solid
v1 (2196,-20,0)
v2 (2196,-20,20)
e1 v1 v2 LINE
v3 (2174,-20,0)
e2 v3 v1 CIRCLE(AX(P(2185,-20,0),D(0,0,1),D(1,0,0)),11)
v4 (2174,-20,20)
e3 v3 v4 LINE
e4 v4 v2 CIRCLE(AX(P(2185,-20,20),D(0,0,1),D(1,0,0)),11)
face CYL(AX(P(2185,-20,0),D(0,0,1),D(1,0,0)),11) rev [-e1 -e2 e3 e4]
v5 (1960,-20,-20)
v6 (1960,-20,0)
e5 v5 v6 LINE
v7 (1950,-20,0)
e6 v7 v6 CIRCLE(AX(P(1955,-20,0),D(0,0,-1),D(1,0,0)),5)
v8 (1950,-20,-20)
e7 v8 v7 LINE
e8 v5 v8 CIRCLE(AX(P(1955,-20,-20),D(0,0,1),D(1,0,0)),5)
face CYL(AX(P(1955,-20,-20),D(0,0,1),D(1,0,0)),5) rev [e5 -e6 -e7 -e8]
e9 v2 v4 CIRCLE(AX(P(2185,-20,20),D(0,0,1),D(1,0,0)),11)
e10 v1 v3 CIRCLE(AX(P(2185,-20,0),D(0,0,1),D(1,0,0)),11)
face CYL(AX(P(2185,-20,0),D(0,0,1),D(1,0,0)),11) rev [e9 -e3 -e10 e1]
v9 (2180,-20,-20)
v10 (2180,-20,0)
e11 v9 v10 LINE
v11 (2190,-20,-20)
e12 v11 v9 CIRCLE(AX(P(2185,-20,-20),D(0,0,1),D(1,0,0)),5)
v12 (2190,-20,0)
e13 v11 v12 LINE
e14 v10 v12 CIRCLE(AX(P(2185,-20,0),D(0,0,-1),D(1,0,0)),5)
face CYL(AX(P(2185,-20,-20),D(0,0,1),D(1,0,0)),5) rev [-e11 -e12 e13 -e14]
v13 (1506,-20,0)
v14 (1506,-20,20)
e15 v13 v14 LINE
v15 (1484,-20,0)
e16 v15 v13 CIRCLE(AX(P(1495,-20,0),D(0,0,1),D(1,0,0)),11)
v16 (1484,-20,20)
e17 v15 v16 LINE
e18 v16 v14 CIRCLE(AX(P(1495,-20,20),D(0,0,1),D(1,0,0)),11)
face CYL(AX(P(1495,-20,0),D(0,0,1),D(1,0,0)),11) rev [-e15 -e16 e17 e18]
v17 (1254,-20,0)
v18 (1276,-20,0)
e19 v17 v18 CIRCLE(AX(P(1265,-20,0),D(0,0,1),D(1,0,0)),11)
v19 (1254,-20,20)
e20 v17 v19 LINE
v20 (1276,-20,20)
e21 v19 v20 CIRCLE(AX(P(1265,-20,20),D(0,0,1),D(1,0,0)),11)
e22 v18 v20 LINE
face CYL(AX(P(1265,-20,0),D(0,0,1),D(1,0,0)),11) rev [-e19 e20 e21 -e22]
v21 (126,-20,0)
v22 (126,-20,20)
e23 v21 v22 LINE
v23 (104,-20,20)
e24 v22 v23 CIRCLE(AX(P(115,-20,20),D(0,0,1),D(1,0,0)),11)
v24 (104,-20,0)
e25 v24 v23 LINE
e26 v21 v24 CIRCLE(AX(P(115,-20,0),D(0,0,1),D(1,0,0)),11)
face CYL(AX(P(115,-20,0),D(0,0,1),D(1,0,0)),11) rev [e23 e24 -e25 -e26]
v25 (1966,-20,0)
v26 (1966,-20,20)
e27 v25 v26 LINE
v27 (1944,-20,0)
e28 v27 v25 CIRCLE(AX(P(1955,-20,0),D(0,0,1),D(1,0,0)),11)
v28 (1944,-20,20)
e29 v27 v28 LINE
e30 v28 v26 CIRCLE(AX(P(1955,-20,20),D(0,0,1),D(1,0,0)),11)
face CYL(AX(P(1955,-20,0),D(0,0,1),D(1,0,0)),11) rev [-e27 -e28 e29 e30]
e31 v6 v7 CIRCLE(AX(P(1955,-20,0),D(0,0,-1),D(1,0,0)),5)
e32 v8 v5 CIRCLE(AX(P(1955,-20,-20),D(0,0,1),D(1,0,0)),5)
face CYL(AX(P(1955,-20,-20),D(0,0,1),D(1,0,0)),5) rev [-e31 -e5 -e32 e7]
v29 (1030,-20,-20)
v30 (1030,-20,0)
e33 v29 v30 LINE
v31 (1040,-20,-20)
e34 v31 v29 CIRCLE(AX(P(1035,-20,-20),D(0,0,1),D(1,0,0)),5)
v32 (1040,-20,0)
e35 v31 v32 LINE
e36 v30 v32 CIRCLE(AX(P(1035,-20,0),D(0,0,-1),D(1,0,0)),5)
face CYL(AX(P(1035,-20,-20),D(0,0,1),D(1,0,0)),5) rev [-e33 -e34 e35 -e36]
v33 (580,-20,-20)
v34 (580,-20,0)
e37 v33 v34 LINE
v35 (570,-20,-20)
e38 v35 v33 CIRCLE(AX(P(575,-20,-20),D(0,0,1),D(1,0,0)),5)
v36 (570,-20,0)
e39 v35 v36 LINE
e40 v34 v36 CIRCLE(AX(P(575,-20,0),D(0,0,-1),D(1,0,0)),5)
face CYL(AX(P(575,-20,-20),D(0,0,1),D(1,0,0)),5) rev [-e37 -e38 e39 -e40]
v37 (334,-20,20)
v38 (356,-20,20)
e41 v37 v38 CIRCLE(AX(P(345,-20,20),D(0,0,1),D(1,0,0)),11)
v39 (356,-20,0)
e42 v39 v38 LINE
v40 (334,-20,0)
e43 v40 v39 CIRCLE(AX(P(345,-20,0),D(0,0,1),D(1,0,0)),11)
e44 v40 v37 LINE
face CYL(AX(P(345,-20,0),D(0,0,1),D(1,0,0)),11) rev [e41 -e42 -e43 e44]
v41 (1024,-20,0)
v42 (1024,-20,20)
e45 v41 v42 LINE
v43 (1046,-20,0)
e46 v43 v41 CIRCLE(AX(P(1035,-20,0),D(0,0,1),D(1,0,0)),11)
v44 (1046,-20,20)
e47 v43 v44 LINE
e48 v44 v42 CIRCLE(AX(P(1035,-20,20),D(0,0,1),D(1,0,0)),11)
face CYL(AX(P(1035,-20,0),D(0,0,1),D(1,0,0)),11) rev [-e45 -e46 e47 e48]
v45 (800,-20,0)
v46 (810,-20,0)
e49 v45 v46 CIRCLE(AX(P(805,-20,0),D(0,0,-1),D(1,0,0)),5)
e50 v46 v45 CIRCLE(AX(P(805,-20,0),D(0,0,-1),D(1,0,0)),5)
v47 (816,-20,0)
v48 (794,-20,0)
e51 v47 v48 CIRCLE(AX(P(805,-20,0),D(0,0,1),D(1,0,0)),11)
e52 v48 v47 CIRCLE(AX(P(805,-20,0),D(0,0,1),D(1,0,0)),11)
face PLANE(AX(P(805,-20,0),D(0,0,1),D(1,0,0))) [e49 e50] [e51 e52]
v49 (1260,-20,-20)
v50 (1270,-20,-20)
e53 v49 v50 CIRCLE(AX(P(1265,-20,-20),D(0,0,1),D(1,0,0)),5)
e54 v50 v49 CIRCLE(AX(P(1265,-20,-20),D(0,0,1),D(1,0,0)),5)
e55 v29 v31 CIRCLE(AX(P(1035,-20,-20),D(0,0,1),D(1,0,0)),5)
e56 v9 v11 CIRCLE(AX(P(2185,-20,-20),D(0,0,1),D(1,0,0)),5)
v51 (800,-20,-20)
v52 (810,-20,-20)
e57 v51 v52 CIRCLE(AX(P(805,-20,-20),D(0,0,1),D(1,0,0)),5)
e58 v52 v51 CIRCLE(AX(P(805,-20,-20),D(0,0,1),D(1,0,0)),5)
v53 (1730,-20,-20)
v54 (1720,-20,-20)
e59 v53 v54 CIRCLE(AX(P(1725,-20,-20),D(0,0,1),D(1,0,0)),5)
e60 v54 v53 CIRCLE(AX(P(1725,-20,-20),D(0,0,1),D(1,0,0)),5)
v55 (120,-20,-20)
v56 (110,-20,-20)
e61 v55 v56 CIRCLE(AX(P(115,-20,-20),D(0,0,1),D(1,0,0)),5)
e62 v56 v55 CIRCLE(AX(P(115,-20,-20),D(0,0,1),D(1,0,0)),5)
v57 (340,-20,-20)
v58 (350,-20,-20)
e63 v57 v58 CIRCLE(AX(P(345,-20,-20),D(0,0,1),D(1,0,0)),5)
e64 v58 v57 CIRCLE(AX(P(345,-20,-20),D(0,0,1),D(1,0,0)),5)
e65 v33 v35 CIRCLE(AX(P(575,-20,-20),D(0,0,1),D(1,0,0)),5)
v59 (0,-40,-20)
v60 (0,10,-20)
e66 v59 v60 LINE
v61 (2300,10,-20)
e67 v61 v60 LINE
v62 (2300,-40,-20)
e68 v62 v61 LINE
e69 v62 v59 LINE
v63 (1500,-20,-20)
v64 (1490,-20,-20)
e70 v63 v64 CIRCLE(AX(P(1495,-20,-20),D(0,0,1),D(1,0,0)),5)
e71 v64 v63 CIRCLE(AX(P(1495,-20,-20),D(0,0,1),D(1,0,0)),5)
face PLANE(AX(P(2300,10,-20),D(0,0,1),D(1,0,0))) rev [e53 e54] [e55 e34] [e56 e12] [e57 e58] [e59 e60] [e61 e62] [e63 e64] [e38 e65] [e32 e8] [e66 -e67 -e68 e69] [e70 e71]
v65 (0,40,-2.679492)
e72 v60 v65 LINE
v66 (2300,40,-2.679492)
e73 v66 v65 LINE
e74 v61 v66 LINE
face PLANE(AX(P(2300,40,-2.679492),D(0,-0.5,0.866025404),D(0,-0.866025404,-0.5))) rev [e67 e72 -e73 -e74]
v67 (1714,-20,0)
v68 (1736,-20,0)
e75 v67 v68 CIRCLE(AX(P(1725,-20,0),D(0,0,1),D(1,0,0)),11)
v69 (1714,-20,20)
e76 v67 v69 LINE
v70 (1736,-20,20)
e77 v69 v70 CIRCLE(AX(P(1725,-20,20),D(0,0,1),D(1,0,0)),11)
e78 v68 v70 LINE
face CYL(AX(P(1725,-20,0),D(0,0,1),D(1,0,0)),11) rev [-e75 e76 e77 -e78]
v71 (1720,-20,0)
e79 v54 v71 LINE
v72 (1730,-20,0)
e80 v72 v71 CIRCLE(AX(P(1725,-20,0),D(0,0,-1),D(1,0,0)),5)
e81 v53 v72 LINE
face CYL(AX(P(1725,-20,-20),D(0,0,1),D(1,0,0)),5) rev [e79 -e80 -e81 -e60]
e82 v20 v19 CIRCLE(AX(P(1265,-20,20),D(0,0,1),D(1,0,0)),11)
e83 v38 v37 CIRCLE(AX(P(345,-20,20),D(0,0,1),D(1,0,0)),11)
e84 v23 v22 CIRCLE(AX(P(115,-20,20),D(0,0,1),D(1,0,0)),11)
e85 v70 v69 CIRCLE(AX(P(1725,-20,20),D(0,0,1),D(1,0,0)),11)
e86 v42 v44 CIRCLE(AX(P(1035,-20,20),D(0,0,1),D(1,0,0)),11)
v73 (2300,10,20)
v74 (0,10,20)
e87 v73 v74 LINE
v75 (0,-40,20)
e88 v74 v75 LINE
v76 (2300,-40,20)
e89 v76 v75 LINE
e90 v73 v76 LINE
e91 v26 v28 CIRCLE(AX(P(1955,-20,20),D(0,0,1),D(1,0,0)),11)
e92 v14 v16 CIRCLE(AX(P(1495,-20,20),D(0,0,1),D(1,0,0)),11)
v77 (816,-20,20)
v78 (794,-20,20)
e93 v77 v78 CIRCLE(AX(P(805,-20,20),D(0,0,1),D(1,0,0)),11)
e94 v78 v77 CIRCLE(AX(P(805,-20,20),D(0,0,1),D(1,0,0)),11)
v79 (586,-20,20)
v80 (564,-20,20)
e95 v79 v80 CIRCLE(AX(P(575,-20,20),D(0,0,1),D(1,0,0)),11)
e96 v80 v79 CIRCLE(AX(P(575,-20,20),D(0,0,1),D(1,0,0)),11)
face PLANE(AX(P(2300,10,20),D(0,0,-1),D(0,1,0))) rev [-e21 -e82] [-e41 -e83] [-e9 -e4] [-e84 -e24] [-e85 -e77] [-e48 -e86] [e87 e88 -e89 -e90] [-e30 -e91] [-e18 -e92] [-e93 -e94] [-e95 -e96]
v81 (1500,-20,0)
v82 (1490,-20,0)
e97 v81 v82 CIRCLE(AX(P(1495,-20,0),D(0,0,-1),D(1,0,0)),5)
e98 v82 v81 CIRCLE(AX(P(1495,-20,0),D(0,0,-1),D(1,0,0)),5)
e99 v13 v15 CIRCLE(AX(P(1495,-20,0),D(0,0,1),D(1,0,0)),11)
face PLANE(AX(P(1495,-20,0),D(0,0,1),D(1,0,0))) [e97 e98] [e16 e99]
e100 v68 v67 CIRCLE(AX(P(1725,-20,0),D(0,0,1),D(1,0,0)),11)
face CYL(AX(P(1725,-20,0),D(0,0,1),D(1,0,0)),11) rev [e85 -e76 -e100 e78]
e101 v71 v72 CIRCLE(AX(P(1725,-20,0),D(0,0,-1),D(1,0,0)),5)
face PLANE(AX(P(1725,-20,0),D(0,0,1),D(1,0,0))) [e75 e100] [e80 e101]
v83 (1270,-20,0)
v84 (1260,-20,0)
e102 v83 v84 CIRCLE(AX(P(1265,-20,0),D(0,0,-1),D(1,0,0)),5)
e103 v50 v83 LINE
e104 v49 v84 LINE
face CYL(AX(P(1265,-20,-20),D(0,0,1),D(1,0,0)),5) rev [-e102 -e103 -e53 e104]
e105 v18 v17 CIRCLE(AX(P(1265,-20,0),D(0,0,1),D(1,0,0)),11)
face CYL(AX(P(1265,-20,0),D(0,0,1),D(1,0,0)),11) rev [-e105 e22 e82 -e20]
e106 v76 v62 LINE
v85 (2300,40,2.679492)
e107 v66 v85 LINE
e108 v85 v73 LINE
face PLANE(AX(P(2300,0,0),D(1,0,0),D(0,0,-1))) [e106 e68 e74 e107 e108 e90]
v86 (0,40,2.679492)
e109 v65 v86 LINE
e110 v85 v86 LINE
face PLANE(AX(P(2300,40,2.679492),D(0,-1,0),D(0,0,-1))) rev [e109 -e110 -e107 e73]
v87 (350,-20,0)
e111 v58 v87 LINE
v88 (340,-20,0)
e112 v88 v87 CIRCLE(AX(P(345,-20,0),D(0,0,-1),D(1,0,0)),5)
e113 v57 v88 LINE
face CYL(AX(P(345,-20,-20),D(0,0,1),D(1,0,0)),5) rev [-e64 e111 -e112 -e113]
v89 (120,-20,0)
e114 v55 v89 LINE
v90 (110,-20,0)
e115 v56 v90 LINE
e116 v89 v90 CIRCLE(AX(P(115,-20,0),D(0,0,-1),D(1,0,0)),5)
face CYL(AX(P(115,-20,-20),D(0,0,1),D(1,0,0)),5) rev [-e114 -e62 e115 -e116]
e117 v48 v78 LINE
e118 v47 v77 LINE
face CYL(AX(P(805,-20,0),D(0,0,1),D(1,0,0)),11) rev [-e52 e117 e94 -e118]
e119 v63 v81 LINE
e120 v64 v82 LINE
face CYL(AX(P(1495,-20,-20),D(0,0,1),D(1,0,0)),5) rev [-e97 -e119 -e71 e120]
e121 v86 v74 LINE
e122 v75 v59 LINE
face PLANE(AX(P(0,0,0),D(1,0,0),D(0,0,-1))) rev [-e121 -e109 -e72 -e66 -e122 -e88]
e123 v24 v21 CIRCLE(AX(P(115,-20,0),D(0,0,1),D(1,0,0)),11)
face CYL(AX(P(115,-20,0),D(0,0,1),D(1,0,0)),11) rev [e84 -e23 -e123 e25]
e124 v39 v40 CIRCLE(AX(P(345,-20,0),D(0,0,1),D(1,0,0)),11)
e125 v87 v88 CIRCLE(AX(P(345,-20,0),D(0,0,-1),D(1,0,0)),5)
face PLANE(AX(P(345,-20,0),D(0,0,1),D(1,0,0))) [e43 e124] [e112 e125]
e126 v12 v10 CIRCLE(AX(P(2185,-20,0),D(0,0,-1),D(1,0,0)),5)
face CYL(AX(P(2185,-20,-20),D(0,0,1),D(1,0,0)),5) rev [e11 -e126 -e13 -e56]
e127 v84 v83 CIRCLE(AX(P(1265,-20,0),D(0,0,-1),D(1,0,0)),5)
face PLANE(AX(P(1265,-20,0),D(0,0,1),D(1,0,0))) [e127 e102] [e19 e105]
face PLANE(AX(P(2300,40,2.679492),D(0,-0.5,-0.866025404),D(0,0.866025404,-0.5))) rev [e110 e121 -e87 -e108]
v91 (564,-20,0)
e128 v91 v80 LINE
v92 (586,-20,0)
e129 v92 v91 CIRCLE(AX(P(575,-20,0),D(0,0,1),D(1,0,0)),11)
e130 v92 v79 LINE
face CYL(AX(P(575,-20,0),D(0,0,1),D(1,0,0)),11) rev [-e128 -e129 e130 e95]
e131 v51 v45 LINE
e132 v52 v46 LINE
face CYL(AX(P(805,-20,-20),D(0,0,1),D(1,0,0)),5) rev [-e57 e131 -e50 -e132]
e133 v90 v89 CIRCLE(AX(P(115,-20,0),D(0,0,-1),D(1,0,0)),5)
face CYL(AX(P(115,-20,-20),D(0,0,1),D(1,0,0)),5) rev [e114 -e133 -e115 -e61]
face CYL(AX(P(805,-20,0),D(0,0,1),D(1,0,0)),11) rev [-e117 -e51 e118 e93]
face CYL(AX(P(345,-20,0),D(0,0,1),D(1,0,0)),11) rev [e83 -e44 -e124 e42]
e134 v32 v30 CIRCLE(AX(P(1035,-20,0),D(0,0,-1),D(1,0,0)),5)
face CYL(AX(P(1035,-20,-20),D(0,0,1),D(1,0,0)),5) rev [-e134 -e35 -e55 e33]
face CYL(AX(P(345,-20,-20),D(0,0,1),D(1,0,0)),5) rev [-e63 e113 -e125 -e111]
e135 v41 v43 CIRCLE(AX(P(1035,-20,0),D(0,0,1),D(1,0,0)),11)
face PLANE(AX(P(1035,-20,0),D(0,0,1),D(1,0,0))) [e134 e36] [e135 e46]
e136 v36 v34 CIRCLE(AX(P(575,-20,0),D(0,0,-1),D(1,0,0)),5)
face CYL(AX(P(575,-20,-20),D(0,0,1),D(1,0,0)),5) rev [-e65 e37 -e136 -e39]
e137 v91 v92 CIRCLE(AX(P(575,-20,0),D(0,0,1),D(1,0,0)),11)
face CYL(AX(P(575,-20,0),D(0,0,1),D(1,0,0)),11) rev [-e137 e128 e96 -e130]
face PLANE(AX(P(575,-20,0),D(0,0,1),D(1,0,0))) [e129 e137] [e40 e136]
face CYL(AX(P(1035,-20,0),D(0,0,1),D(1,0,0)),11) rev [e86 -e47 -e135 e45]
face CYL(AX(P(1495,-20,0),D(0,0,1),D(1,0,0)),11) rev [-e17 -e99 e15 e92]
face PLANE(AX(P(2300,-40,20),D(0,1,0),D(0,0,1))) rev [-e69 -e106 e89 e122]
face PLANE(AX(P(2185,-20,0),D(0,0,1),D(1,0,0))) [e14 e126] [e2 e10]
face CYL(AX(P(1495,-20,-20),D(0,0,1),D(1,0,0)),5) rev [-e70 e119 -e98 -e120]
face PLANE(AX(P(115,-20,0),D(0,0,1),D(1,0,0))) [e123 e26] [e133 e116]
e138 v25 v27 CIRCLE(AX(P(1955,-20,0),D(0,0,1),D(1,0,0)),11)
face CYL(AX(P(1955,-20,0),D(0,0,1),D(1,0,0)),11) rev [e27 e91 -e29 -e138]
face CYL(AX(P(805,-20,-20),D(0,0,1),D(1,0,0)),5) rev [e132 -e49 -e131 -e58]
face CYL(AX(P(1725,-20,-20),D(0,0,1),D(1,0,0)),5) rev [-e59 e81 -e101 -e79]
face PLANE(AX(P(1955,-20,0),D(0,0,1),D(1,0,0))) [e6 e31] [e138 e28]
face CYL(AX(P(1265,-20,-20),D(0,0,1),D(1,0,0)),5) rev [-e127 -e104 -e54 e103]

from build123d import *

# Parameters (mm, degrees)
BOSS_EXTRUDE1_DEPTH = 2300
SKETCH2_R           = 5
CUT_EXTRUDE1_DEPTH  = 2301.695547003
SKETCH3_R           = 11
CUT_EXTRUDE2_DEPTH  = 20
LPATTERN1_COUNT     = 10
LPATTERN1_PITCH     = 230


with BuildPart() as part:
    # Sketch1 → Boss-Extrude1 (new body)
    with BuildSketch(Plane(origin=(0, 0, 0), x_dir=(0, 0, -1), z_dir=(1, 0, 0))):
        Polygon((-2.679491924, 40), (-20, 10), (-20, -40), (20, -40), (20, 10), (2.679491924, 40), align=None)
    extrude(amount=BOSS_EXTRUDE1_DEPTH)

    # Sketch2 → Cut-Extrude1 (cut, through all)
    with BuildSketch(Plane.XY.offset(20)):
        with Locations((115, -20)):
            Circle(SKETCH2_R)
    cut_extrude1 = extrude(amount=-CUT_EXTRUDE1_DEPTH, mode=Mode.SUBTRACT)

    # Sketch3 → Cut-Extrude2 (cut)
    with BuildSketch(Plane.XY.offset(20)):
        with Locations((115, -20)):
            Circle(SKETCH3_R)
    cut_extrude2 = extrude(amount=-CUT_EXTRUDE2_DEPTH, mode=Mode.SUBTRACT)

    # LPattern1: Cut-Extrude1, Cut-Extrude2 ×10
    with Locations(*[(i * LPATTERN1_PITCH, 0, 0) for i in range(1, LPATTERN1_COUNT)]):
        add(cut_extrude1, mode=Mode.SUBTRACT)
        add(cut_extrude2, mode=Mode.SUBTRACT)


solid = part.part
